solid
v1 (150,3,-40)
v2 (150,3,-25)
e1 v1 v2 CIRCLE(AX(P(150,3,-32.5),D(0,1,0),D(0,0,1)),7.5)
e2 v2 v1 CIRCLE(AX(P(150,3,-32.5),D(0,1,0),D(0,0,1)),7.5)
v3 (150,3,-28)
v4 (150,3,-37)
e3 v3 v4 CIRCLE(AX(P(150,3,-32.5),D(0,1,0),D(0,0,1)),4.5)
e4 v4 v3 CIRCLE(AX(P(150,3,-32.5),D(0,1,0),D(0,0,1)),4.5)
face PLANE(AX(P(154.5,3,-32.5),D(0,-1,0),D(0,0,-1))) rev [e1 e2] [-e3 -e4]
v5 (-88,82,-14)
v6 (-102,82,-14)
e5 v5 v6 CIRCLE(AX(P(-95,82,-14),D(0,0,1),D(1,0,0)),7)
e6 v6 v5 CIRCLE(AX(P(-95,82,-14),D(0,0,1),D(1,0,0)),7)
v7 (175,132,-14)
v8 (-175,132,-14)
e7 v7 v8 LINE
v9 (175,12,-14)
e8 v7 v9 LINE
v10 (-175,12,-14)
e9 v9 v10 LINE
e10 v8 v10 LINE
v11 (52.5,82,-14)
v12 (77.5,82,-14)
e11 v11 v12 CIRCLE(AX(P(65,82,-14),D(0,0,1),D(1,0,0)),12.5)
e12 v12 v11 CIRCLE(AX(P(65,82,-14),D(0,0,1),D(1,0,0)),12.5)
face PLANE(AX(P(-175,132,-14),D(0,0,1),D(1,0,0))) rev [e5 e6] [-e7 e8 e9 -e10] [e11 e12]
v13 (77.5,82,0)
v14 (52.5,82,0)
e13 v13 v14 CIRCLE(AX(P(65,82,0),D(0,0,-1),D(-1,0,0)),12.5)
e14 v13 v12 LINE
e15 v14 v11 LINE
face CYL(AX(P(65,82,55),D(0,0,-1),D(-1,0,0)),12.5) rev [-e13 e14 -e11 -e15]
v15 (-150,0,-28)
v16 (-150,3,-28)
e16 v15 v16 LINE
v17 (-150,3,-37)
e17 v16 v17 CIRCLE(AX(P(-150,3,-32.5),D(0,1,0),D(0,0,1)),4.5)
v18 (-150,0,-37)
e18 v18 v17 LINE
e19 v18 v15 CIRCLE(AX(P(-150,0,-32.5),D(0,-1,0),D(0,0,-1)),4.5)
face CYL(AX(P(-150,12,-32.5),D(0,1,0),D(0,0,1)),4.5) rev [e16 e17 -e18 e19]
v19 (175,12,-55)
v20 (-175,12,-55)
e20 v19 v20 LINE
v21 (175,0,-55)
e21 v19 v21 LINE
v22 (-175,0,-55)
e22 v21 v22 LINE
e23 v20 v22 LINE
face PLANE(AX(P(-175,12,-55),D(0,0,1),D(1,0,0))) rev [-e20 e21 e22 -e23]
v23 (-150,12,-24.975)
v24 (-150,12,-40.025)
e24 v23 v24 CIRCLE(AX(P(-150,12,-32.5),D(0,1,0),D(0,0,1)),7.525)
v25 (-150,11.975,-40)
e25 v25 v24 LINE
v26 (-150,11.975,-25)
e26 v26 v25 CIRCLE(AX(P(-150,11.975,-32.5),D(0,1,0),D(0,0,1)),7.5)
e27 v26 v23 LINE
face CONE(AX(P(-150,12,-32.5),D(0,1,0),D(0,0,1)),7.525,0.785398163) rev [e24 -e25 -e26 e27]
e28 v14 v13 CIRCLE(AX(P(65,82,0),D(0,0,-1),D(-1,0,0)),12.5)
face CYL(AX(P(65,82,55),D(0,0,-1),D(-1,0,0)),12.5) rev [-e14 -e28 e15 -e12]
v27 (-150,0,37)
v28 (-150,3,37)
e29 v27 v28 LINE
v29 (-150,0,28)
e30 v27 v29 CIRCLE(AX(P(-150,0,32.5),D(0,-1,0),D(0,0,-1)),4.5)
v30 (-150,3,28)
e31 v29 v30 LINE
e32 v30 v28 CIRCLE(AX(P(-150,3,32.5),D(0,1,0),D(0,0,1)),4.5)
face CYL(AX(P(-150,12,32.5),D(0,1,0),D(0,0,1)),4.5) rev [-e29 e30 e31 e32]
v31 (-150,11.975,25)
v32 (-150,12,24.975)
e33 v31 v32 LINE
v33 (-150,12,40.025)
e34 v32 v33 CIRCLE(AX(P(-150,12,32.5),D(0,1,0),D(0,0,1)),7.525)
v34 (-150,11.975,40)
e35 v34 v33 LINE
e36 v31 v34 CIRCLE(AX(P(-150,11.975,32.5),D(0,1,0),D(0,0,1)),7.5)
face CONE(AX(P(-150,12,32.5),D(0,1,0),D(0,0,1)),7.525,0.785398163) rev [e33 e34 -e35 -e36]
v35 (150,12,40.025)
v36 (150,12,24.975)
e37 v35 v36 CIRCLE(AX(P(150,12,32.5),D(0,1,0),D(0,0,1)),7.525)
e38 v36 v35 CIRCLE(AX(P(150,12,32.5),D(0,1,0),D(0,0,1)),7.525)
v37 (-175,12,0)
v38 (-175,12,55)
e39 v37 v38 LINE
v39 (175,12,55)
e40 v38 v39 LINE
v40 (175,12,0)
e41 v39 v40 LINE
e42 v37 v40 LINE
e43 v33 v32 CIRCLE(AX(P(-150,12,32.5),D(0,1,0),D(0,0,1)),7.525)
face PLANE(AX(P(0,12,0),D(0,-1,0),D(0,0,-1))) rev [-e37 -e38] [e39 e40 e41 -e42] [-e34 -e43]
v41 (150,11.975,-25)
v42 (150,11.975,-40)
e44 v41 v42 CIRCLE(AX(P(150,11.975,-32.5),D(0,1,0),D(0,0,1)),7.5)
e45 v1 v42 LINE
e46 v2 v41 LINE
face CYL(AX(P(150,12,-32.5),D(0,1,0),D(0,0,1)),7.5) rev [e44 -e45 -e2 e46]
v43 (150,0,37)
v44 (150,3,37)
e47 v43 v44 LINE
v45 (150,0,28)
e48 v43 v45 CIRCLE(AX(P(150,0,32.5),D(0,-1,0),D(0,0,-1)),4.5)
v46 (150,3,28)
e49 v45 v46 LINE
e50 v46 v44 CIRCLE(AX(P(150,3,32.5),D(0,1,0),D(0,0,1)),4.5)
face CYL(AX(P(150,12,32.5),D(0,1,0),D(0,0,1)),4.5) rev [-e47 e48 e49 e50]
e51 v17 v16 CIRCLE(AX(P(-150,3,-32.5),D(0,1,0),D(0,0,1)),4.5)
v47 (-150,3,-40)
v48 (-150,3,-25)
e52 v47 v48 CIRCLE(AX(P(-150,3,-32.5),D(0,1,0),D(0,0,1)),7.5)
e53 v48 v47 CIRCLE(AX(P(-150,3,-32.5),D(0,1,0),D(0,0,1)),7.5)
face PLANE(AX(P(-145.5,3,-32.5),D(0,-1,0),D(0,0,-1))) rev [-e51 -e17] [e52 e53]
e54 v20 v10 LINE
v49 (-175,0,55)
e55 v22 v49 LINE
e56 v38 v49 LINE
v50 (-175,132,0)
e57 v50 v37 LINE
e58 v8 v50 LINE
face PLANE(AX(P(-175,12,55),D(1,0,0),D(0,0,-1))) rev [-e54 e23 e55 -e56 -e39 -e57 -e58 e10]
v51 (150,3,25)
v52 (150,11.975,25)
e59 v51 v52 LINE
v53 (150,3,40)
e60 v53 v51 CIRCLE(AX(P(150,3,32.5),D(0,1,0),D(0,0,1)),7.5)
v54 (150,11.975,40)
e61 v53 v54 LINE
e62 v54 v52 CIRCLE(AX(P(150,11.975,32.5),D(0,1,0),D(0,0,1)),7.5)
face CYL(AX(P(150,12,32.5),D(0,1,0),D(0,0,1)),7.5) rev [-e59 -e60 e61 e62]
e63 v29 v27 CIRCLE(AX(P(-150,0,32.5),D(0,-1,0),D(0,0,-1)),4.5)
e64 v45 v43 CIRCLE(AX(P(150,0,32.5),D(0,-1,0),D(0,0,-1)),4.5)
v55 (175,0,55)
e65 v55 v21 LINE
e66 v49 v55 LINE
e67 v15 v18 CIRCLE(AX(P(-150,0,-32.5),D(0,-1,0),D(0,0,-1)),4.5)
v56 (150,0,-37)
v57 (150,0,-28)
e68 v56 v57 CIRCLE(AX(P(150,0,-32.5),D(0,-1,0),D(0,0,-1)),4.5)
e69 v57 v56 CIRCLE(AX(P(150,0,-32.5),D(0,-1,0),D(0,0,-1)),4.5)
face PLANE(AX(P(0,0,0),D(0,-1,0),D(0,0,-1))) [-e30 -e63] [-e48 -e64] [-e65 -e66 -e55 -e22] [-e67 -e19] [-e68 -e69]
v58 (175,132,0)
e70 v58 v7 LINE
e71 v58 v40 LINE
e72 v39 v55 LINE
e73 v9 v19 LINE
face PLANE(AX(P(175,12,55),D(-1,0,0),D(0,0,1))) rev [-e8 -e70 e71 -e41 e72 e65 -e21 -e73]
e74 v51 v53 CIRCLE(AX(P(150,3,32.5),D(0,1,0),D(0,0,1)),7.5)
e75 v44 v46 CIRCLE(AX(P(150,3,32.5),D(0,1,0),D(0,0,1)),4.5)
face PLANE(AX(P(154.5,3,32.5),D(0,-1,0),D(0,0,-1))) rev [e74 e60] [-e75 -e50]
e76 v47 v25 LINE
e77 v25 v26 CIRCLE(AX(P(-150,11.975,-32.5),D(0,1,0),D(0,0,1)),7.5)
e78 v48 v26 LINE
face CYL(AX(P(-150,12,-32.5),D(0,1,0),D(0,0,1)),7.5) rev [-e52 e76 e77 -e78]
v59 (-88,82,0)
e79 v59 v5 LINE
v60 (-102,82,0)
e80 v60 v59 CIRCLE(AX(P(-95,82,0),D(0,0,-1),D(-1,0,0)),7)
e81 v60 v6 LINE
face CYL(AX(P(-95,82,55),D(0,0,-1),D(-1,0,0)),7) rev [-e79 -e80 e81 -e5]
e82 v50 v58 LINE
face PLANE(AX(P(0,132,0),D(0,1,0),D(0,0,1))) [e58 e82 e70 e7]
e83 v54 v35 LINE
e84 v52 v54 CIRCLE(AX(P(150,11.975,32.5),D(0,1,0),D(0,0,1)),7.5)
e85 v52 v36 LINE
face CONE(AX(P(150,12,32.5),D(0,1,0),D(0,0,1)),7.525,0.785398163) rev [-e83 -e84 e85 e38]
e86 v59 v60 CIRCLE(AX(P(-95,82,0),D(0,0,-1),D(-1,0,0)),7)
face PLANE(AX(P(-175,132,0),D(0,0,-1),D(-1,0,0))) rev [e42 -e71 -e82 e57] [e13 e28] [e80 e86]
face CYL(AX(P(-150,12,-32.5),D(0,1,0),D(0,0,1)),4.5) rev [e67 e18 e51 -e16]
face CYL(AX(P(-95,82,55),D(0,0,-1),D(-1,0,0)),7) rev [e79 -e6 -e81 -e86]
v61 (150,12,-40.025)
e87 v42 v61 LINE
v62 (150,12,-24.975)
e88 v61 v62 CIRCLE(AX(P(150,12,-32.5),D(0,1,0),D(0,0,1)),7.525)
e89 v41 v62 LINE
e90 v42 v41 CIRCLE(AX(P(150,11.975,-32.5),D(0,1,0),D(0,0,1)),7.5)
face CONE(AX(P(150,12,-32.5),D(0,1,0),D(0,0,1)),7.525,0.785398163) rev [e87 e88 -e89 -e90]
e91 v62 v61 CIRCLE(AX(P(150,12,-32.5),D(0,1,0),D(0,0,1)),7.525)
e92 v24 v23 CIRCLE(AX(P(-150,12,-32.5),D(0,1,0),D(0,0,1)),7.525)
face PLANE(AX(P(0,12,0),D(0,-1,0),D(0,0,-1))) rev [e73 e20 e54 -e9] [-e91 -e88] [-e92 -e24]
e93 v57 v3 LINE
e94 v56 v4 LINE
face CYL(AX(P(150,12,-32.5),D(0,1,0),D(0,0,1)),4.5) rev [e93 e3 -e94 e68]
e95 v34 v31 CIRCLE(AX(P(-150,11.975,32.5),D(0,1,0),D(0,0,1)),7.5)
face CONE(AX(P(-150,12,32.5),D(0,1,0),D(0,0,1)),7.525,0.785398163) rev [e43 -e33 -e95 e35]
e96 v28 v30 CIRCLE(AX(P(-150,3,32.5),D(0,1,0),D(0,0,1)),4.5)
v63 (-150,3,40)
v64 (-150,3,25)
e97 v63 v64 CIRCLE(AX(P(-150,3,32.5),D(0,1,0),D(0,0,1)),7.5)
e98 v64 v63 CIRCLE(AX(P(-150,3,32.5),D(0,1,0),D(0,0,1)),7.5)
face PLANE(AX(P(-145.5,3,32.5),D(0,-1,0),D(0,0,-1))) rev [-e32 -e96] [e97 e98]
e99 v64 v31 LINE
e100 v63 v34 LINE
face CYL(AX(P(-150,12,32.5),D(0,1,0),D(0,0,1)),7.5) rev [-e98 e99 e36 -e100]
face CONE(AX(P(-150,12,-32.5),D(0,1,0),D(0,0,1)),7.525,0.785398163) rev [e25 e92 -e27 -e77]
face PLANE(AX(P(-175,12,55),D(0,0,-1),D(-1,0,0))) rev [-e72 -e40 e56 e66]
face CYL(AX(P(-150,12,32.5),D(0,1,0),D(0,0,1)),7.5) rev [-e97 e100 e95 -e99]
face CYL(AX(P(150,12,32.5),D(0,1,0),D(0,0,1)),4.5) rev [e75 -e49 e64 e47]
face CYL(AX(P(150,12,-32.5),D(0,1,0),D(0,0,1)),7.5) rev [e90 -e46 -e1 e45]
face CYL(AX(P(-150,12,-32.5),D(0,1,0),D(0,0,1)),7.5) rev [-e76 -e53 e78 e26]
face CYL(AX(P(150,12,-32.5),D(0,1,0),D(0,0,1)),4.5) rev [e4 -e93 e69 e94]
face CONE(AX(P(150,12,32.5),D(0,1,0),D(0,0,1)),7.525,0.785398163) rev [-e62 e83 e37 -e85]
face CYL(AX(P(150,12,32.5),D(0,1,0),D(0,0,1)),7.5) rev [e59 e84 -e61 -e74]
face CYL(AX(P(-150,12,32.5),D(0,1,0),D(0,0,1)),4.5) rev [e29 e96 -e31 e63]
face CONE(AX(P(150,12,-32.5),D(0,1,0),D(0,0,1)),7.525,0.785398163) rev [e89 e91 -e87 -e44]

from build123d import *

# Parameters (mm, degrees)
SKETCH1_W                                    = 350
SKETCH1_H                                    = 110
BOSS_EXTRUDE1_DEPTH                          = 12
SKETCH2_W                                    = 350
SKETCH2_H                                    = 14
BOSS_EXTRUDE2_DEPTH                          = 120
CBORE_FOR_M8_HEXAGON_SOCKET_HEAD_CAP_2_COUNT = 2
CBORE_FOR_M8_HEXAGON_SOCKET_HEAD_CAP_2_PITCH = 65
CBORE_FOR_M8_HEXAGON_SOCKET_HEAD_CAP_3_COUNT = 2
CBORE_FOR_M8_HEXAGON_SOCKET_HEAD_CAP_3_PITCH = 300
CBORE_FOR_M8_HEXAGON_SOCKET_HEAD_CAP_4_COUNT = 2
CBORE_FOR_M8_HEXAGON_SOCKET_HEAD_CAP_4_PITCH = 306.960909563
CUT_EXTRUDE1_DEPTH                           = 230.804264538
CUT_EXTRUDE1_DEPTH_BACK                      = 230.804264538
SKETCH6_R                                    = 7
CUT_EXTRUDE2_DEPTH                           = 230.804264538
CUT_EXTRUDE2_DEPTH_BACK                      = 230.804264538
SKETCH7_R                                    = 12.5


with BuildPart() as part:
    # Sketch1 → Boss-Extrude1 (new body)
    with BuildSketch(Plane(origin=(0, 0, 0), x_dir=(1, 0, 0), z_dir=(0, 1, 0))):
        Rectangle(SKETCH1_W, SKETCH1_H)
    extrude(amount=BOSS_EXTRUDE1_DEPTH)

    # Sketch2 → Boss-Extrude2 (add)
    with BuildSketch(Plane(origin=(0, 12, 0), x_dir=(1, 0, 0), z_dir=(0, 1, 0))):
        with Locations((0, 7)):
            Rectangle(SKETCH2_W, SKETCH2_H)
    extrude(amount=BOSS_EXTRUDE2_DEPTH)

    # Sketch4 → CBORE for M8 Hexagon socket head cap screws1 (revolve, cut)
    with BuildSketch(Plane(origin=(-150, 12, -32.5), x_dir=(0, 0, 1), z_dir=(1, 0, 0))):
        Polygon((0, 0), (0, 15.103872786), (4.5, 12.4), (4.5, 9), (7.5, 9), (7.5, 0.025), (7.525, 0), align=None)
    cbore_for_m8_hexagon_socket_head_cap_scr = revolve(axis=Axis((-150, 18.35, -32.5), (0, -1, 0)), mode=Mode.SUBTRACT)

    # CBORE for M8 Hexagon socket head cap 2: CBORE for M8 Hexagon socket head cap screws1 ×2
    with Locations(*[(0, 0, i * CBORE_FOR_M8_HEXAGON_SOCKET_HEAD_CAP_2_PITCH) for i in range(1, CBORE_FOR_M8_HEXAGON_SOCKET_HEAD_CAP_2_COUNT)]):
        add(cbore_for_m8_hexagon_socket_head_cap_scr, mode=Mode.SUBTRACT)

    # CBORE for M8 Hexagon socket head cap 3: CBORE for M8 Hexagon socket head cap screws1 ×2
    with Locations(*[(i * CBORE_FOR_M8_HEXAGON_SOCKET_HEAD_CAP_3_PITCH, 0, 0) for i in range(1, CBORE_FOR_M8_HEXAGON_SOCKET_HEAD_CAP_3_COUNT)]):
        add(cbore_for_m8_hexagon_socket_head_cap_scr, mode=Mode.SUBTRACT)

    # CBORE for M8 Hexagon socket head cap 4: CBORE for M8 Hexagon socket head cap screws1 ×2
    with Locations(*[Vector(0.9773231400267972, 0, 0.21175334700580606) * (i * CBORE_FOR_M8_HEXAGON_SOCKET_HEAD_CAP_4_PITCH) for i in range(1, CBORE_FOR_M8_HEXAGON_SOCKET_HEAD_CAP_4_COUNT)]):
        add(cbore_for_m8_hexagon_socket_head_cap_scr, mode=Mode.SUBTRACT)

    # Sketch6 → Cut-Extrude1 (cut, two sides: drawn at the far end of the back side and taken through both)
    with BuildSketch(Plane(origin=(0, 0, -14), x_dir=(-1, 0, 0), z_dir=(0, 0, -1)).offset(-CUT_EXTRUDE1_DEPTH_BACK)):
        with Locations((95, 82)):
            Circle(SKETCH6_R)
    extrude(amount=CUT_EXTRUDE1_DEPTH + CUT_EXTRUDE1_DEPTH_BACK, mode=Mode.SUBTRACT)

    # Sketch7 → Cut-Extrude2 (cut, two sides: drawn at the far end of the back side and taken through both)
    with BuildSketch(Plane(origin=(0, 0, -14), x_dir=(-1, 0, 0), z_dir=(0, 0, -1)).offset(-CUT_EXTRUDE2_DEPTH_BACK)):
        with Locations((-65, 82)):
            Circle(SKETCH7_R)
    extrude(amount=CUT_EXTRUDE2_DEPTH + CUT_EXTRUDE2_DEPTH_BACK, mode=Mode.SUBTRACT)


solid = part.part
